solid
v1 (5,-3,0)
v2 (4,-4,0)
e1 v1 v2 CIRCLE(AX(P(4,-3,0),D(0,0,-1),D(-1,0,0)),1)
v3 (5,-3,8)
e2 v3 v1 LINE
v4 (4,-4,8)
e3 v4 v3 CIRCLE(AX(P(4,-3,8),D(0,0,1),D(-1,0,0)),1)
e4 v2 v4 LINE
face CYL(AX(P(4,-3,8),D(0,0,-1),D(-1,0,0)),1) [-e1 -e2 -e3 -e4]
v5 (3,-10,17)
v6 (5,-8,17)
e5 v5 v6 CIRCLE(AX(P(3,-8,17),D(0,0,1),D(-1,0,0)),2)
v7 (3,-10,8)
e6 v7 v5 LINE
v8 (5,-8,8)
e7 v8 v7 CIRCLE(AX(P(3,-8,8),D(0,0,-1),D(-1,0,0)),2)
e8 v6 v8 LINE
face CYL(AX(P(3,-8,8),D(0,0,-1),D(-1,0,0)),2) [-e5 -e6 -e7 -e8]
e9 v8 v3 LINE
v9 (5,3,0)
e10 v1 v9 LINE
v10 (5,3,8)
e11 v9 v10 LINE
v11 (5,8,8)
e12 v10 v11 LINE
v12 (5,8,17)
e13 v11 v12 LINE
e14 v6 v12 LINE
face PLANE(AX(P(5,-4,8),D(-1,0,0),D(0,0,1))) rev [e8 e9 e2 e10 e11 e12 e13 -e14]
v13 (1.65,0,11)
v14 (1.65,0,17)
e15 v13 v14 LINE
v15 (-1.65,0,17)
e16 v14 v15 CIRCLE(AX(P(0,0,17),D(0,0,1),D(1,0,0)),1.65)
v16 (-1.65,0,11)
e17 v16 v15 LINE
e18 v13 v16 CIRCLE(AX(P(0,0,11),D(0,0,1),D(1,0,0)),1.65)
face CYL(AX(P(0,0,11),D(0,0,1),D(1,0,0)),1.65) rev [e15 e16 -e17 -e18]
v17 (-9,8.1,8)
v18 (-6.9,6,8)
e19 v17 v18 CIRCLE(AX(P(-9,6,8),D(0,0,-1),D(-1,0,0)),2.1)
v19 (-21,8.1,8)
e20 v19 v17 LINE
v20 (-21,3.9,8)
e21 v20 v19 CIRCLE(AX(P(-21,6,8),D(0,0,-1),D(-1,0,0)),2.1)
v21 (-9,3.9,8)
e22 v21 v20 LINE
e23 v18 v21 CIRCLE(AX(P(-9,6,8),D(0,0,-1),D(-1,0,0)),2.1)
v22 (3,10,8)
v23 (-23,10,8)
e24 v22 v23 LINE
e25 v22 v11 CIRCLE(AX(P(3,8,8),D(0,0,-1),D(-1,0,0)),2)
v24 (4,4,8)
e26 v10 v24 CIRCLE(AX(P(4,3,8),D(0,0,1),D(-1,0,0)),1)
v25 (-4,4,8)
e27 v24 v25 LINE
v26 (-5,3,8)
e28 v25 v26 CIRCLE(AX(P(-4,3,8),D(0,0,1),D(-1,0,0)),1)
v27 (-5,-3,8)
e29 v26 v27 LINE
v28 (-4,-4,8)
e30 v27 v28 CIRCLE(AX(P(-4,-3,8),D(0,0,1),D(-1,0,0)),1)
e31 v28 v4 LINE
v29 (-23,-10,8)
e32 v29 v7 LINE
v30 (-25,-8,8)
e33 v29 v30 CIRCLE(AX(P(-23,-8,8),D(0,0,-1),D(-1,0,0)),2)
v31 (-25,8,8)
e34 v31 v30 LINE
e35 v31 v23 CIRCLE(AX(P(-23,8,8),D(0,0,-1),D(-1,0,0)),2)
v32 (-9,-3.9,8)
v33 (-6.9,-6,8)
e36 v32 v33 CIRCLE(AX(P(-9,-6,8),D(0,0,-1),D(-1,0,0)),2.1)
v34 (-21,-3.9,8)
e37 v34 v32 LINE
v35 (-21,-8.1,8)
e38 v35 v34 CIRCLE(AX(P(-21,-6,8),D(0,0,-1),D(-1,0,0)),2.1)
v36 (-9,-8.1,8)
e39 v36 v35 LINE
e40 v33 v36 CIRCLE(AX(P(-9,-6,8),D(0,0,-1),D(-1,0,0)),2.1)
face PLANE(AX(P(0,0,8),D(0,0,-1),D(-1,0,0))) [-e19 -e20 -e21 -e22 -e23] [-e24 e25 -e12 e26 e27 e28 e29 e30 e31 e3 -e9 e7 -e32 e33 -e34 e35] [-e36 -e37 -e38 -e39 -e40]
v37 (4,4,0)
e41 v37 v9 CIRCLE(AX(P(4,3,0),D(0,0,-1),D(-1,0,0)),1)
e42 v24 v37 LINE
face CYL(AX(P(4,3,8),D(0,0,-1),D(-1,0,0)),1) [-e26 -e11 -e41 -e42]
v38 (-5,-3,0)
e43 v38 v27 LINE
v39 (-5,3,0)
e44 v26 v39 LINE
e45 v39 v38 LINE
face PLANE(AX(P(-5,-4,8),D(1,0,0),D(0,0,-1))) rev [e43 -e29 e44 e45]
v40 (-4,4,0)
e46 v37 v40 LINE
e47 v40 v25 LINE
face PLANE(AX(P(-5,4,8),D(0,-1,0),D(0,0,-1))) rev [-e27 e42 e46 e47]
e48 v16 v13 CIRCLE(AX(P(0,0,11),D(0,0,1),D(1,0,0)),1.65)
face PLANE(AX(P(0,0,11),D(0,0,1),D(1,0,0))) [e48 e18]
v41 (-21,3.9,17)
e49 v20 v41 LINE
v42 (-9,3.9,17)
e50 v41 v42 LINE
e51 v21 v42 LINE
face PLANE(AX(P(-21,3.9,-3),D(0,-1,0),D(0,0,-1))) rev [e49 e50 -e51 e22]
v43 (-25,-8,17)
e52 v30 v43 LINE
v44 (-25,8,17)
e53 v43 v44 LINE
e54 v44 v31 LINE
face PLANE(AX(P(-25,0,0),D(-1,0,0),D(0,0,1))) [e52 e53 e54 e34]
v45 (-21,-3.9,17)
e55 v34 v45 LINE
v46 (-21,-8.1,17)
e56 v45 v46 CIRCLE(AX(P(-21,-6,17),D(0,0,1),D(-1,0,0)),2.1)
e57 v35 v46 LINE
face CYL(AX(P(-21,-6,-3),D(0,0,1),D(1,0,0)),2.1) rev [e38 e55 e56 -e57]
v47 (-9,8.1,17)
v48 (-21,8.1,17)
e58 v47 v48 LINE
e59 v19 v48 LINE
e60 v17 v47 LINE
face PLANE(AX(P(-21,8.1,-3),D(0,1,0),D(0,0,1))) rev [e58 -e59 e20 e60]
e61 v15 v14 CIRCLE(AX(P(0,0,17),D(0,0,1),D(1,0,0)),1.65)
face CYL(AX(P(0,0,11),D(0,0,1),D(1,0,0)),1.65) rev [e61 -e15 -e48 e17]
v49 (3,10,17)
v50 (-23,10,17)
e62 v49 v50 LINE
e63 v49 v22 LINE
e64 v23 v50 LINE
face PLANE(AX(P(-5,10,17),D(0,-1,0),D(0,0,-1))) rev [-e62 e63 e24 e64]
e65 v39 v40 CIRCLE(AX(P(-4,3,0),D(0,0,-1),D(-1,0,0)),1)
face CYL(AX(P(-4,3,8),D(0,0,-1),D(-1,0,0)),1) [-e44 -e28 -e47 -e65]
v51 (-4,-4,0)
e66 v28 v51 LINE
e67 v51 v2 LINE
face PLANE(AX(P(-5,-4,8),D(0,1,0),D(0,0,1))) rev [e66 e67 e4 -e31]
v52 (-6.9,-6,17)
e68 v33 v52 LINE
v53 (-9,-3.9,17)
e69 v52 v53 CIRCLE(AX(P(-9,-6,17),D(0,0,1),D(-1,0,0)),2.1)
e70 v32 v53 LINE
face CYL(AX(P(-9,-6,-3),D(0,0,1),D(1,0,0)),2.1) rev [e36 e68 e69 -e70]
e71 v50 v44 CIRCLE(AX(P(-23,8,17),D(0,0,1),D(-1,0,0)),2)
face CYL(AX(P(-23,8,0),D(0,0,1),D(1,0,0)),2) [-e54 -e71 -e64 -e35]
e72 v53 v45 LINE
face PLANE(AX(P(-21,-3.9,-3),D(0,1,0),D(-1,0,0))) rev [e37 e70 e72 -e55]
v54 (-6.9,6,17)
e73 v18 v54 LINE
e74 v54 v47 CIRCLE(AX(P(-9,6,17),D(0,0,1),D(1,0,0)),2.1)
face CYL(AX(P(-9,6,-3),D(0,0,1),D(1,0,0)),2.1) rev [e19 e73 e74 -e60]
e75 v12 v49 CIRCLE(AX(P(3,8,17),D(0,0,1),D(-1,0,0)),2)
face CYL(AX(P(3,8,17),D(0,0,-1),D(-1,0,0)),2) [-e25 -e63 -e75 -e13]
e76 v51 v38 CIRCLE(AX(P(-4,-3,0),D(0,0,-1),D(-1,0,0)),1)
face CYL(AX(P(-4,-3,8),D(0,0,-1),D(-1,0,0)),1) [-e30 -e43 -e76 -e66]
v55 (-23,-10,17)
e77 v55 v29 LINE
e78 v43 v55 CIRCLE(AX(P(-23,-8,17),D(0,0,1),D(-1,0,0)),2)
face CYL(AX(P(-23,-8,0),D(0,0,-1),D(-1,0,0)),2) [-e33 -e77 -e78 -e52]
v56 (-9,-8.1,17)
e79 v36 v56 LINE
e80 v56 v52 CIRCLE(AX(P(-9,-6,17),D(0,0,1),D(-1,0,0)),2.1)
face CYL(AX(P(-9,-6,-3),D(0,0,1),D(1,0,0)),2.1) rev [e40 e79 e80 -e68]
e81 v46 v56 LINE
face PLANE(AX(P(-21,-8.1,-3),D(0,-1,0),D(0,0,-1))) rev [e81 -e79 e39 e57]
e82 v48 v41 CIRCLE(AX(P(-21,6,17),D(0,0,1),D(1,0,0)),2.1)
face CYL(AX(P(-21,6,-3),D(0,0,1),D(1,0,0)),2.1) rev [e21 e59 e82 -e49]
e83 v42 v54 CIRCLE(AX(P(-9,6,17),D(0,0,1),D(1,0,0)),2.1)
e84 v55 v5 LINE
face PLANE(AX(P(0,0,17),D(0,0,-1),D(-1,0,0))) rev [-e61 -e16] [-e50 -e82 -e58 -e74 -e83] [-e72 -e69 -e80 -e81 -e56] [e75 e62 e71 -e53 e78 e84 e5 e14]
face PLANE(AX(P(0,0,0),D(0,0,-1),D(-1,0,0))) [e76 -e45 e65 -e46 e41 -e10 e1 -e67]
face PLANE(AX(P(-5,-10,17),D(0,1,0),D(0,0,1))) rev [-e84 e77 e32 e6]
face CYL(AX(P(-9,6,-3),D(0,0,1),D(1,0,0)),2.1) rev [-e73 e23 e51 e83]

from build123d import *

# Parameters (mm, degrees)
SKETCH_1_W          = 10
SKETCH_1_H          = 8
EXTRUDE_1_DEPTH     = 8
SKETCH_2_W          = 10
SKETCH_2_H          = 20
EXTRUDE_2_DEPTH     = 9
SKETCH_4_R          = 1.65
CUT_EXTRUDE_2_DEPTH = 6
SKETCH_7_W          = 9
SKETCH_7_H          = 20
EXTRUDE_3_DEPTH     = 20
CUT_EXTRUDE_5_DEPTH = 20
FILLET_2_R          = 2
FILLET_3_R          = 1


with BuildPart() as part:
    # 草图1 → 凸台-拉伸1 (new body)
    with BuildSketch(Plane.XY):
        Rectangle(SKETCH_1_W, SKETCH_1_H)
    extrude(amount=EXTRUDE_1_DEPTH)

    # 草图2 → 凸台-拉伸2 (add)
    with BuildSketch(Plane.XY.offset(8)):
        Rectangle(SKETCH_2_W, SKETCH_2_H)
    extrude(amount=EXTRUDE_2_DEPTH)

    # 草图4 → 切除-拉伸2 (cut)
    with BuildSketch(Plane.XY.offset(17)):
        Circle(SKETCH_4_R)
    extrude(amount=-CUT_EXTRUDE_2_DEPTH, mode=Mode.SUBTRACT)

    # 草图7 → 凸台-拉伸3 (add)
    with BuildSketch(Plane.ZY.offset(5)):
        with Locations((12.5, 0)):
            Rectangle(SKETCH_7_W, SKETCH_7_H)
    extrude(amount=EXTRUDE_3_DEPTH)

    # 草图8 → 切除-拉伸5 (cut)
    with BuildSketch(Plane.XY.offset(17)):
        with BuildLine():
            Line((-21, 8.1), (-9, 8.1))
            ThreePointArc((-9, 8.1), (-6.9, 6), (-9, 3.9))
            Line((-9, 3.9), (-21, 3.9))
            ThreePointArc((-21, 3.9), (-23.1, 6), (-21, 8.1))
        make_face()
        with BuildLine():
            Line((-21, -8.1), (-9, -8.1))
            ThreePointArc((-9, -8.1), (-6.9, -6), (-9, -3.9))
            Line((-9, -3.9), (-21, -3.9))
            ThreePointArc((-21, -3.9), (-23.1, -6), (-21, -8.1))
        make_face()
    extrude(amount=-CUT_EXTRUDE_5_DEPTH, mode=Mode.SUBTRACT)

    # 圆角2
    fillet_2_edges = [part.edges().sort_by_distance(p)[0] for p in [
        (5, -10, 12.5),
        (5, 10, 12.5),
        (-25, -10, 12.5),
        (-25, 10, 12.5),
    ]]
    fillet(fillet_2_edges, radius=FILLET_2_R)

    # 圆角3
    fillet_3_edges = [part.edges().sort_by_distance(p)[0] for p in [
        (5, -4, 4),
        (-5, -4, 4),
        (-5, 4, 4),
        (5, 4, 4),
    ]]
    fillet(fillet_3_edges, radius=FILLET_3_R)


solid = part.part
